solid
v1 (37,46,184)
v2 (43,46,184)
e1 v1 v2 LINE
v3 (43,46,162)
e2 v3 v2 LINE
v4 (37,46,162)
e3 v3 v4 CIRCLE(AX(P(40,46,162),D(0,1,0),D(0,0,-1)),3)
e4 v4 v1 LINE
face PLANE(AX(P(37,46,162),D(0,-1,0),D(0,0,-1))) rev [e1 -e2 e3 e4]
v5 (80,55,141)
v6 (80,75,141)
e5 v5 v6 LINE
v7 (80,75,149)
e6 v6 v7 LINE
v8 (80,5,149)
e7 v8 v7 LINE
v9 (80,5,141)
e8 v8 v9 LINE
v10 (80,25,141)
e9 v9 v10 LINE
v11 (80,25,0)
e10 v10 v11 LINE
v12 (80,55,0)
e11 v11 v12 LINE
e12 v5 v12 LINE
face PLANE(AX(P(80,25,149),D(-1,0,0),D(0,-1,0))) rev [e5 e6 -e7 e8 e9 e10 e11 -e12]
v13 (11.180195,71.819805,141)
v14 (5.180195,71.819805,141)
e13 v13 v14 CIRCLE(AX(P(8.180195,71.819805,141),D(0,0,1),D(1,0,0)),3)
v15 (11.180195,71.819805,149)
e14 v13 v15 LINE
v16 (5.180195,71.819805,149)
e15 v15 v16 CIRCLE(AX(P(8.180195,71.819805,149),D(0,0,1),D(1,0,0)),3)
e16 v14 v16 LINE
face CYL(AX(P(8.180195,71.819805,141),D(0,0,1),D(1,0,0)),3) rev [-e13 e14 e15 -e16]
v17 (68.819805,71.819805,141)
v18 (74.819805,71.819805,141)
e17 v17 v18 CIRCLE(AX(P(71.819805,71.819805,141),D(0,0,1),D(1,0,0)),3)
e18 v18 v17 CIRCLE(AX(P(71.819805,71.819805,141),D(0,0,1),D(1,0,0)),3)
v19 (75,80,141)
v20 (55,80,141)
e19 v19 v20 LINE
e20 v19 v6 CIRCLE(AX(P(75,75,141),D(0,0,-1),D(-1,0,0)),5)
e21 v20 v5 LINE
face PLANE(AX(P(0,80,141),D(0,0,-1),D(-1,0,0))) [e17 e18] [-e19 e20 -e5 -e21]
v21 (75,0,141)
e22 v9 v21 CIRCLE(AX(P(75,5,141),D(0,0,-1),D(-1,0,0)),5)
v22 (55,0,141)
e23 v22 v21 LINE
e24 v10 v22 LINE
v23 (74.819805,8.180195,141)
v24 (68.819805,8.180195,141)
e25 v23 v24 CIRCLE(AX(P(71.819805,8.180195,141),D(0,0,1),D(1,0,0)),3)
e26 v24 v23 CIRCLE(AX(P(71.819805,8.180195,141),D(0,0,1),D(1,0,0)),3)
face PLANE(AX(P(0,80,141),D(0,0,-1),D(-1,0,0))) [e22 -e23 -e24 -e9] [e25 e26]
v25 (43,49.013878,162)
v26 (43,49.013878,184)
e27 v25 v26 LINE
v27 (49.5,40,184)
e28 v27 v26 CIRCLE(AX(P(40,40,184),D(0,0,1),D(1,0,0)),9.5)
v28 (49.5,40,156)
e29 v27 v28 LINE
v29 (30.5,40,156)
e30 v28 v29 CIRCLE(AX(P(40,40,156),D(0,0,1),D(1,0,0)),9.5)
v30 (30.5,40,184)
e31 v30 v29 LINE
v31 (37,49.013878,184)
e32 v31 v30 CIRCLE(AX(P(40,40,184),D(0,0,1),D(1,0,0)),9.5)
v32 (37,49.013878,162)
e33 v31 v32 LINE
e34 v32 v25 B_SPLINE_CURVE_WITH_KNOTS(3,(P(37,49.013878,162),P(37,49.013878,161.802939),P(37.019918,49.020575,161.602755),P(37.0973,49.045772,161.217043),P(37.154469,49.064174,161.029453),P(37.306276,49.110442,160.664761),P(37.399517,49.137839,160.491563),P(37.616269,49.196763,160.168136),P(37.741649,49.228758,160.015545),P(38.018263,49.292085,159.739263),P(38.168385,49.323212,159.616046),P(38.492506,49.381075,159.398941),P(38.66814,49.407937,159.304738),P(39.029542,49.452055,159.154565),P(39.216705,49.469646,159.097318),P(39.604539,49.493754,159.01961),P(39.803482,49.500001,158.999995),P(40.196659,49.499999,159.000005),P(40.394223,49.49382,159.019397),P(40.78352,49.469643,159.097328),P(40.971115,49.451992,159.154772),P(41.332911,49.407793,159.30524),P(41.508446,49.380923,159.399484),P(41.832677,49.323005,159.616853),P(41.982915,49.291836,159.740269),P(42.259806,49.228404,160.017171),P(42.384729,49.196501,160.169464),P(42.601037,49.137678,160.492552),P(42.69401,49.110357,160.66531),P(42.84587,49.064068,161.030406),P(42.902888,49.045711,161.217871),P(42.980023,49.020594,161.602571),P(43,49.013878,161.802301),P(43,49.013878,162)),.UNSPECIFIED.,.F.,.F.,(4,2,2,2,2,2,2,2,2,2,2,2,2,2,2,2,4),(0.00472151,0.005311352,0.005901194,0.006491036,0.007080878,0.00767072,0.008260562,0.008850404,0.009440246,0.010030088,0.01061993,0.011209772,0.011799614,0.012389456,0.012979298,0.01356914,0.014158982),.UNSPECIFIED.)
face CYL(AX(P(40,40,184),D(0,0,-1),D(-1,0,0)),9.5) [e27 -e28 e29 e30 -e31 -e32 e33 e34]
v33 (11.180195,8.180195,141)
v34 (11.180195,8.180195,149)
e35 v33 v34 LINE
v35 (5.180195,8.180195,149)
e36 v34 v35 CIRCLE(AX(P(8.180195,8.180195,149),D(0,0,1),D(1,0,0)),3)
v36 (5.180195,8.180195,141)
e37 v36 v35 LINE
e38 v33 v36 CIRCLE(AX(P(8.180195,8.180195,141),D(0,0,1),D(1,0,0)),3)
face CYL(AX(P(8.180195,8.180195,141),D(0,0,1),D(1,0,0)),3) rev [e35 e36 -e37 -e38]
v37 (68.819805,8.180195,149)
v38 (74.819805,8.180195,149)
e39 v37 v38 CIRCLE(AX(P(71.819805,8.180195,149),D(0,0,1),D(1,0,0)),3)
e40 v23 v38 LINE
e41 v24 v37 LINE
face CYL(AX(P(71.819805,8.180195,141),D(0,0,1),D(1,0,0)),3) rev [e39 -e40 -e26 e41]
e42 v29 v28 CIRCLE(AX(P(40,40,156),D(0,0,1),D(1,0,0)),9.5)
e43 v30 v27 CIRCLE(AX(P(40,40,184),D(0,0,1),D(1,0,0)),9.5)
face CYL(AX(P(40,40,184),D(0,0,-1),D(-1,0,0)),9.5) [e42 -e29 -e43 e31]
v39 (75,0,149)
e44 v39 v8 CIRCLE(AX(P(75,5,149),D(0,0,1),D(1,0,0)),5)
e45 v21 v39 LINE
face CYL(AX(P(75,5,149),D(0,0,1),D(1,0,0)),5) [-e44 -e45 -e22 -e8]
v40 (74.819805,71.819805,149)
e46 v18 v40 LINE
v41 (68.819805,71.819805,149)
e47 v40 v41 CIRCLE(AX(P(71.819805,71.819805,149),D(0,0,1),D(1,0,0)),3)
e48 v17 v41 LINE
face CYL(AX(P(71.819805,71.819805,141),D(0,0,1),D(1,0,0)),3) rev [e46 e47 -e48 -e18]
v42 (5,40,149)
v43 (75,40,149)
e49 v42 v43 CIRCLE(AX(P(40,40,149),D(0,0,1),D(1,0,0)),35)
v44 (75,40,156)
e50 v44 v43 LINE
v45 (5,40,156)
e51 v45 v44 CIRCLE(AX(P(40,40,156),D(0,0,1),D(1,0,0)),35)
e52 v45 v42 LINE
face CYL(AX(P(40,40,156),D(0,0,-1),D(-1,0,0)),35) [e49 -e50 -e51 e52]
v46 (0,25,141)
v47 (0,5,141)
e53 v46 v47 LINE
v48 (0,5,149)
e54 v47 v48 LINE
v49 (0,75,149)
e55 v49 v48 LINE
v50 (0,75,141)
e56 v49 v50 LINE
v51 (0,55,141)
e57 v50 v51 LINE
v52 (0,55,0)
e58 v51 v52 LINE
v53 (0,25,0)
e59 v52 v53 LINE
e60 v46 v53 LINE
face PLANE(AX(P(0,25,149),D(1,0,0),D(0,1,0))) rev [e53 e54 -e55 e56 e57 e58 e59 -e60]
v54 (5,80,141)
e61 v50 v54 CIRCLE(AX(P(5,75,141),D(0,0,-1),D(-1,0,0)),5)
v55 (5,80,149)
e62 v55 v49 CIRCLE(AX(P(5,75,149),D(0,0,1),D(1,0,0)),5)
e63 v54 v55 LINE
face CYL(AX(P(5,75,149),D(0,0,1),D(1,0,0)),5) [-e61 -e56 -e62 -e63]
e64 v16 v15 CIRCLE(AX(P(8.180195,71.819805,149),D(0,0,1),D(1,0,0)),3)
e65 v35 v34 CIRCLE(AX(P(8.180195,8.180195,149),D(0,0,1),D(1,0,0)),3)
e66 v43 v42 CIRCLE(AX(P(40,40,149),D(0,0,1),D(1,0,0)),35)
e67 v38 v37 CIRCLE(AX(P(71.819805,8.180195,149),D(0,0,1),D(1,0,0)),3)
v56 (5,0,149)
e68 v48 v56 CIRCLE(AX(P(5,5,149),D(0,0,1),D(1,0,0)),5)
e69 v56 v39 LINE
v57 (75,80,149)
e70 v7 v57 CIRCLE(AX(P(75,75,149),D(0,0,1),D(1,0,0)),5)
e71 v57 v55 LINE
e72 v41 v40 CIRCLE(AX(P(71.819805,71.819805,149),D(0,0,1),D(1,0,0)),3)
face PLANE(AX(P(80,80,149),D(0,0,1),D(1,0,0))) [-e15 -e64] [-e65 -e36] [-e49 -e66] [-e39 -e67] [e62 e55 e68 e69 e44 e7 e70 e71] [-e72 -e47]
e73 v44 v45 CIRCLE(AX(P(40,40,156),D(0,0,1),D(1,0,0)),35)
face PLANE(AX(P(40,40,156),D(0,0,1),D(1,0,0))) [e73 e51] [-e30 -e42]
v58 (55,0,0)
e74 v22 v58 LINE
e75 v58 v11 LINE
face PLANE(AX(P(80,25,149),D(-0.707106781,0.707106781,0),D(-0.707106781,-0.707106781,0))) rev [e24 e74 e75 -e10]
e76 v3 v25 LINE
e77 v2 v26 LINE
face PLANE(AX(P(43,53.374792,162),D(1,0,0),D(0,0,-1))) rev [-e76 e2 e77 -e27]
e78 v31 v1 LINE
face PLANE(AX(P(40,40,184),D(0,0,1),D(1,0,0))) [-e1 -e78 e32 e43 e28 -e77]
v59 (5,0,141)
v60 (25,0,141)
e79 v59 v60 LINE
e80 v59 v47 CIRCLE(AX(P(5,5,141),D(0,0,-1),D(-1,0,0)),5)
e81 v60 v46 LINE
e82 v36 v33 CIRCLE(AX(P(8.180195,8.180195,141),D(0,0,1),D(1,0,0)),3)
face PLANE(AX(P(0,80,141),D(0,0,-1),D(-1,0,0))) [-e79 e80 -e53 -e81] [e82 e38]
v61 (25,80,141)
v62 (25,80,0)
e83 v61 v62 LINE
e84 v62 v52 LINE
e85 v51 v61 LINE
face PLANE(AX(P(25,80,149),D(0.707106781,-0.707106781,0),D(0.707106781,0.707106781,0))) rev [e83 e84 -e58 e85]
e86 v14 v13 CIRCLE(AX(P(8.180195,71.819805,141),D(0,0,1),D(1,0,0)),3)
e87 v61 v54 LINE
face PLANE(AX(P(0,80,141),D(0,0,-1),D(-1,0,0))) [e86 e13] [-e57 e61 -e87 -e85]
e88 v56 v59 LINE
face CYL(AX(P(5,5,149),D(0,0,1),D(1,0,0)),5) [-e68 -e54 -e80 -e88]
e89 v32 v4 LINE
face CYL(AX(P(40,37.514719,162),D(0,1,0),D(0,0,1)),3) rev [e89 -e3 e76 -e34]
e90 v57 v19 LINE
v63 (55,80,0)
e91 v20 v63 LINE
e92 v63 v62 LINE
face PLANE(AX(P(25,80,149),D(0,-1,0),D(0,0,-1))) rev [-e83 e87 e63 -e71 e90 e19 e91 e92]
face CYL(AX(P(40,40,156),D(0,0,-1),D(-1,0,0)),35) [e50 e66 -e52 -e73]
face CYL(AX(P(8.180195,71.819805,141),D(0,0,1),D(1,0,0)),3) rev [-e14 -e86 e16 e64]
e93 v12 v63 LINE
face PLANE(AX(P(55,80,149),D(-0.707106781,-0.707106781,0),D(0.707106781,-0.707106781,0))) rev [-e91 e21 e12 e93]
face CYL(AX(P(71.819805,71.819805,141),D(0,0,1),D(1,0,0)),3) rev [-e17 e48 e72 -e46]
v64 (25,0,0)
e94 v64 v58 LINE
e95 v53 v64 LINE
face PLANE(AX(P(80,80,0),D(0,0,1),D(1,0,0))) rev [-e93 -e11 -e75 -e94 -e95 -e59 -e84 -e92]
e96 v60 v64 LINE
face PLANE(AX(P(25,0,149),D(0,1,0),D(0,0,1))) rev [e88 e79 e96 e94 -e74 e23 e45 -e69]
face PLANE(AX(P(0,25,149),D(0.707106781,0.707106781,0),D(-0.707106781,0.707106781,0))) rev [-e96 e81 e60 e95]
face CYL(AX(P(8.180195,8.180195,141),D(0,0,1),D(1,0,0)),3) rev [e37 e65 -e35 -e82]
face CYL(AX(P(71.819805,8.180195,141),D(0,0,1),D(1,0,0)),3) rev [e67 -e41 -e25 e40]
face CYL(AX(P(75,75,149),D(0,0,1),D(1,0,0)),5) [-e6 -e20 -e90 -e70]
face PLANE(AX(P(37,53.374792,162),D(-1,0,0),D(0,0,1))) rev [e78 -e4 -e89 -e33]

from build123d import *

# Parameters (mm, degrees)
EXTRUDE_1_DEPTH     = 149
SKETCH_2_R          = 35
EXTRUDE_2_DEPTH     = 7
SKETCH_4_W          = 80
SKETCH_4_H          = 80
EXTRUDE_3_DEPTH     = 8
SKETCH_5_R          = 3
CUT_EXTRUDE_1_DEPTH = 8
FILLET_1_R          = 5
SKETCH_6_R          = 9.5
EXTRUDE_4_DEPTH     = 28
SKETCH_7_W          = 6
SKETCH_7_H          = 7.374792238
EXTRUDE_5_DEPTH     = 22
SKETCH_8_R          = 3
CUT_EXTRUDE_2_DEPTH = 34


with BuildPart() as part:
    # 草图1 → 凸台-拉伸1 (new body)
    with BuildSketch(Plane.XY):
        Polygon((25, 80), (0, 55), (0, 25), (25, 0), (55, 0), (80, 25), (80, 55), (55, 80), align=None)
    extrude(amount=EXTRUDE_1_DEPTH)

    # 草图2 → 凸台-拉伸2 (add)
    with BuildSketch(Plane.XY.offset(149)):
        with Locations((40, 40)):
            Circle(SKETCH_2_R)
    extrude(amount=EXTRUDE_2_DEPTH)

    # 草图4 → 凸台-拉伸3 (add)
    with BuildSketch(Plane.XY.offset(149)):
        with Locations((40, 40)):
            Rectangle(SKETCH_4_W, SKETCH_4_H)
    extrude(amount=-EXTRUDE_3_DEPTH)

    # 草图5 → 切除-拉伸1 (cut)
    with BuildSketch(Plane.XY.offset(149)):
        with Locations((8.180194847, 71.819805153)):
            Circle(SKETCH_5_R)
        with Locations((71.819805153, 71.819805153)):
            Circle(SKETCH_5_R)
        with Locations((71.819805153, 8.180194847)):
            Circle(SKETCH_5_R)
        with Locations((8.180194847, 8.180194847)):
            Circle(SKETCH_5_R)
    extrude(amount=-CUT_EXTRUDE_1_DEPTH, mode=Mode.SUBTRACT)

    # 圆角1
    fillet_1_edges = [part.edges().sort_by_distance(p)[0] for p in [
        (0, 0, 145),
        (80, 0, 145),
        (0, 80, 145),
        (80, 80, 145),
    ]]
    fillet(fillet_1_edges, radius=FILLET_1_R)

    # 草图6 → 凸台-拉伸4 (add)
    with BuildSketch(Plane.XY.offset(156)):
        with Locations((40, 40)):
            Circle(SKETCH_6_R)
    extrude(amount=EXTRUDE_4_DEPTH)


with BuildPart() as body_2:
    # 草图7 → 凸台-拉伸5 (new body)
    with BuildSketch(Plane.XY.offset(184)):
        with Locations((40, 49.687396119)):
            Rectangle(SKETCH_7_W, SKETCH_7_H)
    extrude(amount=-EXTRUDE_5_DEPTH)


with BuildPart() as part_1:
    add(part.part)

    # Combine 1: cut body 2
    add(body_2.part, mode=Mode.SUBTRACT)

    # 草图8 → 切除-拉伸2 (cut)
    with BuildSketch(Plane(origin=(0, 80, 0), x_dir=(1, 0, 0), z_dir=(0, 1, 0))):
        with Locations((40, -162)):
            Circle(SKETCH_8_R)
    extrude(amount=-CUT_EXTRUDE_2_DEPTH, mode=Mode.SUBTRACT)


solid = part_1.part
